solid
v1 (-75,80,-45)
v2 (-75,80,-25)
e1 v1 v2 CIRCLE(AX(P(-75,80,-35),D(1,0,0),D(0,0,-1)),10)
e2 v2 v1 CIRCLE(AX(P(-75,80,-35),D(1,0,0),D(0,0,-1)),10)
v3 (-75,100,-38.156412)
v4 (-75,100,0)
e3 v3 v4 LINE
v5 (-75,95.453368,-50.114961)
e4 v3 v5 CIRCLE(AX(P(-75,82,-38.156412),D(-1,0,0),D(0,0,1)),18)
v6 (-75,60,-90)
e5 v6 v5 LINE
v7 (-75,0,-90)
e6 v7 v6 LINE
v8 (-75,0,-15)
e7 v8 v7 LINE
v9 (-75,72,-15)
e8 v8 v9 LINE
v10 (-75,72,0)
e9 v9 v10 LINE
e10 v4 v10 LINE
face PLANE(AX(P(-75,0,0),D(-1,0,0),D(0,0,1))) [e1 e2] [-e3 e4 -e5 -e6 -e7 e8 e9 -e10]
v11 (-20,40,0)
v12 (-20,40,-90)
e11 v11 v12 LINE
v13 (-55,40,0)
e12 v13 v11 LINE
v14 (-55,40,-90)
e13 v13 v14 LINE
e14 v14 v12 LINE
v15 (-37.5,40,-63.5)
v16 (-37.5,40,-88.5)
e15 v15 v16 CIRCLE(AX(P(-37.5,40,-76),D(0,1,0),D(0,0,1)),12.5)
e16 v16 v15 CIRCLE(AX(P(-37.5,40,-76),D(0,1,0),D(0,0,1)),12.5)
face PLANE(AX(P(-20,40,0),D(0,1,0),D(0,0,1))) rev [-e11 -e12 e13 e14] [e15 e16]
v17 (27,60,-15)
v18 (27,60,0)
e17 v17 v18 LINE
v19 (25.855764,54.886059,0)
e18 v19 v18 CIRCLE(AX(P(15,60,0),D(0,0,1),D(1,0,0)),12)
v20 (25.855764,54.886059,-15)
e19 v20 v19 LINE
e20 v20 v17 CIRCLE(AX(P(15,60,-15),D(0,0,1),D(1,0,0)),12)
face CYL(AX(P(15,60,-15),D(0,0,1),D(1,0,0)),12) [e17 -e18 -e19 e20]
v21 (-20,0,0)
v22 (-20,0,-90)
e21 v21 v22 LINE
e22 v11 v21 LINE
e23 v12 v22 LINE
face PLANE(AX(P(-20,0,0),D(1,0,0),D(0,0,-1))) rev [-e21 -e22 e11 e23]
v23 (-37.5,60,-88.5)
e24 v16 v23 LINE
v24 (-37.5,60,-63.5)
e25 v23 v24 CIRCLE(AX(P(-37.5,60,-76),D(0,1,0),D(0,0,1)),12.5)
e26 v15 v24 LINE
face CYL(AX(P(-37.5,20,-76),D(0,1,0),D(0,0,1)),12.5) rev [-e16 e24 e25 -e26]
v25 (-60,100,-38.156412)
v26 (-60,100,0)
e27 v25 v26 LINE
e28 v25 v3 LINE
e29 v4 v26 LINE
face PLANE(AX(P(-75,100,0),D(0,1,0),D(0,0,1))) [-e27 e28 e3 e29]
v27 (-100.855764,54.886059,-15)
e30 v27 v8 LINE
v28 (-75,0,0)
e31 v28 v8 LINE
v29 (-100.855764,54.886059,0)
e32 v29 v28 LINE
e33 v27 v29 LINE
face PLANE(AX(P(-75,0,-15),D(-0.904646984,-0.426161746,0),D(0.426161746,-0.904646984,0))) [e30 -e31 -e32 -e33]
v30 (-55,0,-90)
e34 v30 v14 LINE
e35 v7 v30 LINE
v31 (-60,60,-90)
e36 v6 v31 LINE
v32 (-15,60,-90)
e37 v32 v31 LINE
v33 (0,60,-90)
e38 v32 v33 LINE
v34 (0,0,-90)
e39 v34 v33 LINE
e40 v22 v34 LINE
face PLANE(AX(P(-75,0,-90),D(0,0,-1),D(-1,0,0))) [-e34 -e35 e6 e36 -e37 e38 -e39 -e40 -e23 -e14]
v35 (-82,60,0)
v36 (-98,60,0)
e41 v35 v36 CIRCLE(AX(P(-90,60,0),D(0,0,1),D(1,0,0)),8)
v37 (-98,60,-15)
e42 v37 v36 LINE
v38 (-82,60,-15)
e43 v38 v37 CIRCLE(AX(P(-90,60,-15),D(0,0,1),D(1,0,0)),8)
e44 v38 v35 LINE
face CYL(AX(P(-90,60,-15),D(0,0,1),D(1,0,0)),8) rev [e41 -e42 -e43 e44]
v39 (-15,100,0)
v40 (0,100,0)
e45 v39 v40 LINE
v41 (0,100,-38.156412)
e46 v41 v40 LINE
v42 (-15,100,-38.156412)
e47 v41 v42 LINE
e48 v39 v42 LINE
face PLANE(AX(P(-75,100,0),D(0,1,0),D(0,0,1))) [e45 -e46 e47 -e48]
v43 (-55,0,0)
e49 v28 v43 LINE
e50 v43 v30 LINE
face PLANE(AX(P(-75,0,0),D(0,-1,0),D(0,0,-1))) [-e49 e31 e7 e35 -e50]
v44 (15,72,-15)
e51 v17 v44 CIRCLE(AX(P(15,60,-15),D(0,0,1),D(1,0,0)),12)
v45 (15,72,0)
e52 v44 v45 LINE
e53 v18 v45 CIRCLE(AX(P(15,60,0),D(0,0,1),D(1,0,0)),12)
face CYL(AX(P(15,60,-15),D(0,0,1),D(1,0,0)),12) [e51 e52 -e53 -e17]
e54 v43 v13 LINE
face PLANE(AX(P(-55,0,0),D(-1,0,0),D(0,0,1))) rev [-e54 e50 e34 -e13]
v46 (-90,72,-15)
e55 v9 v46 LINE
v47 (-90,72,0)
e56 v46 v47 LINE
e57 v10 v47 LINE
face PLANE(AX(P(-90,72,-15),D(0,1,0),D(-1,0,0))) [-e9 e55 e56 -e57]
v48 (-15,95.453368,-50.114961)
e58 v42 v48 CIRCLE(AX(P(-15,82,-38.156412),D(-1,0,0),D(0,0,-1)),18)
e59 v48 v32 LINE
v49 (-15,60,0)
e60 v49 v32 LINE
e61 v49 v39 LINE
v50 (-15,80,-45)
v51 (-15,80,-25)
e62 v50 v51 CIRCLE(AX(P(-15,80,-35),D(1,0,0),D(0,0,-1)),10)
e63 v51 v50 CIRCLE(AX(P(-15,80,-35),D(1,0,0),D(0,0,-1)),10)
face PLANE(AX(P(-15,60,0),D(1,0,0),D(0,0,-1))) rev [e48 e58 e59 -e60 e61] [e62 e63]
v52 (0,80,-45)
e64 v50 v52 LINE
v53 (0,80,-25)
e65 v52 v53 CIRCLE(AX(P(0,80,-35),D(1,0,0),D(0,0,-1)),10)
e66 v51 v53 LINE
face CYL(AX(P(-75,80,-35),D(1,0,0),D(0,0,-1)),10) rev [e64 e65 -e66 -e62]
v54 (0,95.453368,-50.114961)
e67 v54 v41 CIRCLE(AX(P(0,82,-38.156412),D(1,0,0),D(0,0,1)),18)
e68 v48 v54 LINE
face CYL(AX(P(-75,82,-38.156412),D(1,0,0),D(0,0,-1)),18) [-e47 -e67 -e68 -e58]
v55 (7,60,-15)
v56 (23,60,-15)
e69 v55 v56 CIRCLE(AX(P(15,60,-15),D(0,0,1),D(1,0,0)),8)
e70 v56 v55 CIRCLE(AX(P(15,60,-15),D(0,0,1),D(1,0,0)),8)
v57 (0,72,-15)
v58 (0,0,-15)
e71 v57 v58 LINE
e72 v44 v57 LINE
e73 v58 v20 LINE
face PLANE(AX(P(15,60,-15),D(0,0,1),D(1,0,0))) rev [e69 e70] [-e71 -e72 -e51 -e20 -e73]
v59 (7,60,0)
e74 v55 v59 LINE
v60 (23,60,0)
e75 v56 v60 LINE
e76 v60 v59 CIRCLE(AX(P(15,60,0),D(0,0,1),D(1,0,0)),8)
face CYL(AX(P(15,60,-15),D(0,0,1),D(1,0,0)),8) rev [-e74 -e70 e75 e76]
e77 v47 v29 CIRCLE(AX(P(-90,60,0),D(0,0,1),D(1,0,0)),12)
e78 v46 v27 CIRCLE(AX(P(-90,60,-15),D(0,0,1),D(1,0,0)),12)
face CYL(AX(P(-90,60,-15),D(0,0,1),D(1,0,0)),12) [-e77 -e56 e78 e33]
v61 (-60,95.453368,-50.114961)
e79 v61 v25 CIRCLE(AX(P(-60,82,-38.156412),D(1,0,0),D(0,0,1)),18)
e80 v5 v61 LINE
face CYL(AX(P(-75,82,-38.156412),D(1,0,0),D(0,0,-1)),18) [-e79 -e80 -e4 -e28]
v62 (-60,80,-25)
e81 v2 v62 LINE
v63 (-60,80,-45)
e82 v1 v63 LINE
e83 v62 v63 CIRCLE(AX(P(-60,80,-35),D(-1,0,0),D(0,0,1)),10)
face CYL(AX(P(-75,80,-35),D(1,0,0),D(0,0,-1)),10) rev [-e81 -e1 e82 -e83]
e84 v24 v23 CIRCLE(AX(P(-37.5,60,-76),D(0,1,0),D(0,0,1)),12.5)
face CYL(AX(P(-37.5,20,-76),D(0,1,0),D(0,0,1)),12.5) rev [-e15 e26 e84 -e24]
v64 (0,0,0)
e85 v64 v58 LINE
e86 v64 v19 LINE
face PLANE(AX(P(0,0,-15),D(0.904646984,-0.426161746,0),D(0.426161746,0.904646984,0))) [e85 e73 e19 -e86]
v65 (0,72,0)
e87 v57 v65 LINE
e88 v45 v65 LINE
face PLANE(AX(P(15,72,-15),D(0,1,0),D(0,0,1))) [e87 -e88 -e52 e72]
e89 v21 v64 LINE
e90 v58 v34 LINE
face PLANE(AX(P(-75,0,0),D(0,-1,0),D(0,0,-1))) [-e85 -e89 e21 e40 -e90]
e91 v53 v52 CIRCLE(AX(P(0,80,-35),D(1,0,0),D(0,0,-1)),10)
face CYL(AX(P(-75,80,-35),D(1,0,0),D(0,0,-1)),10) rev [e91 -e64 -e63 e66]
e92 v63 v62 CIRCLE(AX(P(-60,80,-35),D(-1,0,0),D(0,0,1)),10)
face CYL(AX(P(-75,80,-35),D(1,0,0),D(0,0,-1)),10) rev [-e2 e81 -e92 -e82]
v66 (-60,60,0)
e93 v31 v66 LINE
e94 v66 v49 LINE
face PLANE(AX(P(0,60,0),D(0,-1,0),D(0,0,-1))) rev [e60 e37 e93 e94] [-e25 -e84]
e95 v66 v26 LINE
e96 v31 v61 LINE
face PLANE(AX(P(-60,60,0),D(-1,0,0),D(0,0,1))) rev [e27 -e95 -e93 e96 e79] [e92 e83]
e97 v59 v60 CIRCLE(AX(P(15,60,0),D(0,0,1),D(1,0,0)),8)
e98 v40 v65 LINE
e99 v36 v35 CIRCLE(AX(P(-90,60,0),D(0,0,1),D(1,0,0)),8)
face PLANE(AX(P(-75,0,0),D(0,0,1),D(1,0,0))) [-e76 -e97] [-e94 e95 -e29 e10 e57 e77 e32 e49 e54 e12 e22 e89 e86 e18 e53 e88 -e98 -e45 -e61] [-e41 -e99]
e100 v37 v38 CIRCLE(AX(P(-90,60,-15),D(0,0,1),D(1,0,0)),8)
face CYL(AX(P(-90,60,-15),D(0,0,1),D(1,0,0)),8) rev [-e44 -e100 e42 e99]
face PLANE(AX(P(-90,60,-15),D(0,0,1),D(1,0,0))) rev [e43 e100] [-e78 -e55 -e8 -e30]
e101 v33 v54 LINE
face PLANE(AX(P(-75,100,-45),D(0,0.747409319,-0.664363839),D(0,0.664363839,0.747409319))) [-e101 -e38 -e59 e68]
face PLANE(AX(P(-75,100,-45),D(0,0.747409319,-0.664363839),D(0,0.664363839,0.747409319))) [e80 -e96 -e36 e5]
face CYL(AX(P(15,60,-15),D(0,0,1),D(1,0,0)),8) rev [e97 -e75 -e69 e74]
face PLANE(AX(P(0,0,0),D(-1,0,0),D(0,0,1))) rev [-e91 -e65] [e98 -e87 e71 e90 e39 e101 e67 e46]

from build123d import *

# Parameters (mm, degrees)
BASE_BLOCK_DEPTH      = 75
BOTTOM_NOTCH_SKETCH_W = 35
BOTTOM_NOTCH_SKETCH_H = 40
BOTTOM_NOTCH_DEPTH    = 155.029218007
TOP_SLOT_SKETCH_W     = 45
TOP_SLOT_SKETCH_H     = 90
TOP_SLOT_DEPTH        = 40
EDGE_FILLET_R18_R     = 18
CROSS_HOLE_SKETCH_R   = 10
CROSS_HOLE_DEPTH      = 155.029218007
PIN_HOLE_SKETCH_R     = 12.5
PIN_HOLE_DEPTH        = 40
SIDE_LUGS_SKETCH_R    = 8
SIDE_LUGS_DEPTH       = 15


with BuildPart() as part:
    # Base Profile Sketch → Base Block (new body)
    with BuildSketch(Plane(origin=(0, 0, 0), x_dir=(0, 0, -1), z_dir=(1, 0, 0))):
        Polygon((0, 0), (90, 0), (90, 60), (45, 100), (0, 100), align=None)
    extrude(amount=-BASE_BLOCK_DEPTH)

    # Bottom Notch Sketch → Bottom Notch (cut, through all)
    with BuildSketch(Plane(origin=(0, 0, -90), x_dir=(-1, 0, 0), z_dir=(0, 0, -1))):
        with Locations((37.5, 20)):
            Rectangle(BOTTOM_NOTCH_SKETCH_W, BOTTOM_NOTCH_SKETCH_H)
    extrude(amount=-BOTTOM_NOTCH_DEPTH, mode=Mode.SUBTRACT)

    # Top Slot Sketch → Top Slot (cut)
    with BuildSketch(Plane(origin=(0, 100, 0), x_dir=(1, 0, 0), z_dir=(0, 1, 0))):
        with Locations((-37.5, 45)):
            Rectangle(TOP_SLOT_SKETCH_W, TOP_SLOT_SKETCH_H)
    extrude(amount=-TOP_SLOT_DEPTH, mode=Mode.SUBTRACT)

    # Edge Fillet R18
    edge_fillet_r18_edges = [part.edges().sort_by_distance(p)[0] for p in [
        (-7.5, 100, -45),
        (-67.5, 100, -45),
    ]]
    fillet(edge_fillet_r18_edges, radius=EDGE_FILLET_R18_R)

    # Cross Hole Sketch → Cross Hole (cut, through all)
    with BuildSketch(Plane(origin=(0, 0, 0), x_dir=(0, 0, -1), z_dir=(1, 0, 0))):
        with Locations((35, 80)):
            Circle(CROSS_HOLE_SKETCH_R)
    extrude(amount=-CROSS_HOLE_DEPTH, mode=Mode.SUBTRACT)

    # Pin Hole Sketch → Pin Hole (cut)
    with BuildSketch(Plane(origin=(0, 60, 0), x_dir=(1, 0, 0), z_dir=(0, 1, 0))):
        with Locations(Location((-37.5, 76, 0), (0, 0, 270))):
            Circle(PIN_HOLE_SKETCH_R)
    extrude(amount=-PIN_HOLE_DEPTH, mode=Mode.SUBTRACT)

    # Side Lugs Sketch → Side Lugs (add)
    # profile 1 of 2: a face of its own
    with BuildSketch(Plane.XY):
        with BuildLine():
            Line((15, 72), (0, 72))
            Line((0, 72), (0, 0))
            Line((0, 0), (25.855763811, 54.886059047))
            ThreePointArc((25.855763811, 54.886059047), (25.133293922, 66.427779888), (15, 72))
        make_face()
        with Locations((15, 60)):
            Circle(SIDE_LUGS_SKETCH_R, mode=Mode.SUBTRACT)
    # profile 2 of 2: a face of its own
    with BuildSketch(Plane.XY):
        with BuildLine():
            Line((-90, 72), (-75, 72))
            Line((-75, 72), (-75, 0))
            Line((-75, 0), (-100.855763811, 54.886059047))
            ThreePointArc((-100.855763811, 54.886059047), (-100.133293922, 66.427779888), (-90, 72))
        make_face()
        with Locations((-90, 60)):
            Circle(SIDE_LUGS_SKETCH_R, mode=Mode.SUBTRACT)
    extrude(amount=-SIDE_LUGS_DEPTH)


solid = part.part
